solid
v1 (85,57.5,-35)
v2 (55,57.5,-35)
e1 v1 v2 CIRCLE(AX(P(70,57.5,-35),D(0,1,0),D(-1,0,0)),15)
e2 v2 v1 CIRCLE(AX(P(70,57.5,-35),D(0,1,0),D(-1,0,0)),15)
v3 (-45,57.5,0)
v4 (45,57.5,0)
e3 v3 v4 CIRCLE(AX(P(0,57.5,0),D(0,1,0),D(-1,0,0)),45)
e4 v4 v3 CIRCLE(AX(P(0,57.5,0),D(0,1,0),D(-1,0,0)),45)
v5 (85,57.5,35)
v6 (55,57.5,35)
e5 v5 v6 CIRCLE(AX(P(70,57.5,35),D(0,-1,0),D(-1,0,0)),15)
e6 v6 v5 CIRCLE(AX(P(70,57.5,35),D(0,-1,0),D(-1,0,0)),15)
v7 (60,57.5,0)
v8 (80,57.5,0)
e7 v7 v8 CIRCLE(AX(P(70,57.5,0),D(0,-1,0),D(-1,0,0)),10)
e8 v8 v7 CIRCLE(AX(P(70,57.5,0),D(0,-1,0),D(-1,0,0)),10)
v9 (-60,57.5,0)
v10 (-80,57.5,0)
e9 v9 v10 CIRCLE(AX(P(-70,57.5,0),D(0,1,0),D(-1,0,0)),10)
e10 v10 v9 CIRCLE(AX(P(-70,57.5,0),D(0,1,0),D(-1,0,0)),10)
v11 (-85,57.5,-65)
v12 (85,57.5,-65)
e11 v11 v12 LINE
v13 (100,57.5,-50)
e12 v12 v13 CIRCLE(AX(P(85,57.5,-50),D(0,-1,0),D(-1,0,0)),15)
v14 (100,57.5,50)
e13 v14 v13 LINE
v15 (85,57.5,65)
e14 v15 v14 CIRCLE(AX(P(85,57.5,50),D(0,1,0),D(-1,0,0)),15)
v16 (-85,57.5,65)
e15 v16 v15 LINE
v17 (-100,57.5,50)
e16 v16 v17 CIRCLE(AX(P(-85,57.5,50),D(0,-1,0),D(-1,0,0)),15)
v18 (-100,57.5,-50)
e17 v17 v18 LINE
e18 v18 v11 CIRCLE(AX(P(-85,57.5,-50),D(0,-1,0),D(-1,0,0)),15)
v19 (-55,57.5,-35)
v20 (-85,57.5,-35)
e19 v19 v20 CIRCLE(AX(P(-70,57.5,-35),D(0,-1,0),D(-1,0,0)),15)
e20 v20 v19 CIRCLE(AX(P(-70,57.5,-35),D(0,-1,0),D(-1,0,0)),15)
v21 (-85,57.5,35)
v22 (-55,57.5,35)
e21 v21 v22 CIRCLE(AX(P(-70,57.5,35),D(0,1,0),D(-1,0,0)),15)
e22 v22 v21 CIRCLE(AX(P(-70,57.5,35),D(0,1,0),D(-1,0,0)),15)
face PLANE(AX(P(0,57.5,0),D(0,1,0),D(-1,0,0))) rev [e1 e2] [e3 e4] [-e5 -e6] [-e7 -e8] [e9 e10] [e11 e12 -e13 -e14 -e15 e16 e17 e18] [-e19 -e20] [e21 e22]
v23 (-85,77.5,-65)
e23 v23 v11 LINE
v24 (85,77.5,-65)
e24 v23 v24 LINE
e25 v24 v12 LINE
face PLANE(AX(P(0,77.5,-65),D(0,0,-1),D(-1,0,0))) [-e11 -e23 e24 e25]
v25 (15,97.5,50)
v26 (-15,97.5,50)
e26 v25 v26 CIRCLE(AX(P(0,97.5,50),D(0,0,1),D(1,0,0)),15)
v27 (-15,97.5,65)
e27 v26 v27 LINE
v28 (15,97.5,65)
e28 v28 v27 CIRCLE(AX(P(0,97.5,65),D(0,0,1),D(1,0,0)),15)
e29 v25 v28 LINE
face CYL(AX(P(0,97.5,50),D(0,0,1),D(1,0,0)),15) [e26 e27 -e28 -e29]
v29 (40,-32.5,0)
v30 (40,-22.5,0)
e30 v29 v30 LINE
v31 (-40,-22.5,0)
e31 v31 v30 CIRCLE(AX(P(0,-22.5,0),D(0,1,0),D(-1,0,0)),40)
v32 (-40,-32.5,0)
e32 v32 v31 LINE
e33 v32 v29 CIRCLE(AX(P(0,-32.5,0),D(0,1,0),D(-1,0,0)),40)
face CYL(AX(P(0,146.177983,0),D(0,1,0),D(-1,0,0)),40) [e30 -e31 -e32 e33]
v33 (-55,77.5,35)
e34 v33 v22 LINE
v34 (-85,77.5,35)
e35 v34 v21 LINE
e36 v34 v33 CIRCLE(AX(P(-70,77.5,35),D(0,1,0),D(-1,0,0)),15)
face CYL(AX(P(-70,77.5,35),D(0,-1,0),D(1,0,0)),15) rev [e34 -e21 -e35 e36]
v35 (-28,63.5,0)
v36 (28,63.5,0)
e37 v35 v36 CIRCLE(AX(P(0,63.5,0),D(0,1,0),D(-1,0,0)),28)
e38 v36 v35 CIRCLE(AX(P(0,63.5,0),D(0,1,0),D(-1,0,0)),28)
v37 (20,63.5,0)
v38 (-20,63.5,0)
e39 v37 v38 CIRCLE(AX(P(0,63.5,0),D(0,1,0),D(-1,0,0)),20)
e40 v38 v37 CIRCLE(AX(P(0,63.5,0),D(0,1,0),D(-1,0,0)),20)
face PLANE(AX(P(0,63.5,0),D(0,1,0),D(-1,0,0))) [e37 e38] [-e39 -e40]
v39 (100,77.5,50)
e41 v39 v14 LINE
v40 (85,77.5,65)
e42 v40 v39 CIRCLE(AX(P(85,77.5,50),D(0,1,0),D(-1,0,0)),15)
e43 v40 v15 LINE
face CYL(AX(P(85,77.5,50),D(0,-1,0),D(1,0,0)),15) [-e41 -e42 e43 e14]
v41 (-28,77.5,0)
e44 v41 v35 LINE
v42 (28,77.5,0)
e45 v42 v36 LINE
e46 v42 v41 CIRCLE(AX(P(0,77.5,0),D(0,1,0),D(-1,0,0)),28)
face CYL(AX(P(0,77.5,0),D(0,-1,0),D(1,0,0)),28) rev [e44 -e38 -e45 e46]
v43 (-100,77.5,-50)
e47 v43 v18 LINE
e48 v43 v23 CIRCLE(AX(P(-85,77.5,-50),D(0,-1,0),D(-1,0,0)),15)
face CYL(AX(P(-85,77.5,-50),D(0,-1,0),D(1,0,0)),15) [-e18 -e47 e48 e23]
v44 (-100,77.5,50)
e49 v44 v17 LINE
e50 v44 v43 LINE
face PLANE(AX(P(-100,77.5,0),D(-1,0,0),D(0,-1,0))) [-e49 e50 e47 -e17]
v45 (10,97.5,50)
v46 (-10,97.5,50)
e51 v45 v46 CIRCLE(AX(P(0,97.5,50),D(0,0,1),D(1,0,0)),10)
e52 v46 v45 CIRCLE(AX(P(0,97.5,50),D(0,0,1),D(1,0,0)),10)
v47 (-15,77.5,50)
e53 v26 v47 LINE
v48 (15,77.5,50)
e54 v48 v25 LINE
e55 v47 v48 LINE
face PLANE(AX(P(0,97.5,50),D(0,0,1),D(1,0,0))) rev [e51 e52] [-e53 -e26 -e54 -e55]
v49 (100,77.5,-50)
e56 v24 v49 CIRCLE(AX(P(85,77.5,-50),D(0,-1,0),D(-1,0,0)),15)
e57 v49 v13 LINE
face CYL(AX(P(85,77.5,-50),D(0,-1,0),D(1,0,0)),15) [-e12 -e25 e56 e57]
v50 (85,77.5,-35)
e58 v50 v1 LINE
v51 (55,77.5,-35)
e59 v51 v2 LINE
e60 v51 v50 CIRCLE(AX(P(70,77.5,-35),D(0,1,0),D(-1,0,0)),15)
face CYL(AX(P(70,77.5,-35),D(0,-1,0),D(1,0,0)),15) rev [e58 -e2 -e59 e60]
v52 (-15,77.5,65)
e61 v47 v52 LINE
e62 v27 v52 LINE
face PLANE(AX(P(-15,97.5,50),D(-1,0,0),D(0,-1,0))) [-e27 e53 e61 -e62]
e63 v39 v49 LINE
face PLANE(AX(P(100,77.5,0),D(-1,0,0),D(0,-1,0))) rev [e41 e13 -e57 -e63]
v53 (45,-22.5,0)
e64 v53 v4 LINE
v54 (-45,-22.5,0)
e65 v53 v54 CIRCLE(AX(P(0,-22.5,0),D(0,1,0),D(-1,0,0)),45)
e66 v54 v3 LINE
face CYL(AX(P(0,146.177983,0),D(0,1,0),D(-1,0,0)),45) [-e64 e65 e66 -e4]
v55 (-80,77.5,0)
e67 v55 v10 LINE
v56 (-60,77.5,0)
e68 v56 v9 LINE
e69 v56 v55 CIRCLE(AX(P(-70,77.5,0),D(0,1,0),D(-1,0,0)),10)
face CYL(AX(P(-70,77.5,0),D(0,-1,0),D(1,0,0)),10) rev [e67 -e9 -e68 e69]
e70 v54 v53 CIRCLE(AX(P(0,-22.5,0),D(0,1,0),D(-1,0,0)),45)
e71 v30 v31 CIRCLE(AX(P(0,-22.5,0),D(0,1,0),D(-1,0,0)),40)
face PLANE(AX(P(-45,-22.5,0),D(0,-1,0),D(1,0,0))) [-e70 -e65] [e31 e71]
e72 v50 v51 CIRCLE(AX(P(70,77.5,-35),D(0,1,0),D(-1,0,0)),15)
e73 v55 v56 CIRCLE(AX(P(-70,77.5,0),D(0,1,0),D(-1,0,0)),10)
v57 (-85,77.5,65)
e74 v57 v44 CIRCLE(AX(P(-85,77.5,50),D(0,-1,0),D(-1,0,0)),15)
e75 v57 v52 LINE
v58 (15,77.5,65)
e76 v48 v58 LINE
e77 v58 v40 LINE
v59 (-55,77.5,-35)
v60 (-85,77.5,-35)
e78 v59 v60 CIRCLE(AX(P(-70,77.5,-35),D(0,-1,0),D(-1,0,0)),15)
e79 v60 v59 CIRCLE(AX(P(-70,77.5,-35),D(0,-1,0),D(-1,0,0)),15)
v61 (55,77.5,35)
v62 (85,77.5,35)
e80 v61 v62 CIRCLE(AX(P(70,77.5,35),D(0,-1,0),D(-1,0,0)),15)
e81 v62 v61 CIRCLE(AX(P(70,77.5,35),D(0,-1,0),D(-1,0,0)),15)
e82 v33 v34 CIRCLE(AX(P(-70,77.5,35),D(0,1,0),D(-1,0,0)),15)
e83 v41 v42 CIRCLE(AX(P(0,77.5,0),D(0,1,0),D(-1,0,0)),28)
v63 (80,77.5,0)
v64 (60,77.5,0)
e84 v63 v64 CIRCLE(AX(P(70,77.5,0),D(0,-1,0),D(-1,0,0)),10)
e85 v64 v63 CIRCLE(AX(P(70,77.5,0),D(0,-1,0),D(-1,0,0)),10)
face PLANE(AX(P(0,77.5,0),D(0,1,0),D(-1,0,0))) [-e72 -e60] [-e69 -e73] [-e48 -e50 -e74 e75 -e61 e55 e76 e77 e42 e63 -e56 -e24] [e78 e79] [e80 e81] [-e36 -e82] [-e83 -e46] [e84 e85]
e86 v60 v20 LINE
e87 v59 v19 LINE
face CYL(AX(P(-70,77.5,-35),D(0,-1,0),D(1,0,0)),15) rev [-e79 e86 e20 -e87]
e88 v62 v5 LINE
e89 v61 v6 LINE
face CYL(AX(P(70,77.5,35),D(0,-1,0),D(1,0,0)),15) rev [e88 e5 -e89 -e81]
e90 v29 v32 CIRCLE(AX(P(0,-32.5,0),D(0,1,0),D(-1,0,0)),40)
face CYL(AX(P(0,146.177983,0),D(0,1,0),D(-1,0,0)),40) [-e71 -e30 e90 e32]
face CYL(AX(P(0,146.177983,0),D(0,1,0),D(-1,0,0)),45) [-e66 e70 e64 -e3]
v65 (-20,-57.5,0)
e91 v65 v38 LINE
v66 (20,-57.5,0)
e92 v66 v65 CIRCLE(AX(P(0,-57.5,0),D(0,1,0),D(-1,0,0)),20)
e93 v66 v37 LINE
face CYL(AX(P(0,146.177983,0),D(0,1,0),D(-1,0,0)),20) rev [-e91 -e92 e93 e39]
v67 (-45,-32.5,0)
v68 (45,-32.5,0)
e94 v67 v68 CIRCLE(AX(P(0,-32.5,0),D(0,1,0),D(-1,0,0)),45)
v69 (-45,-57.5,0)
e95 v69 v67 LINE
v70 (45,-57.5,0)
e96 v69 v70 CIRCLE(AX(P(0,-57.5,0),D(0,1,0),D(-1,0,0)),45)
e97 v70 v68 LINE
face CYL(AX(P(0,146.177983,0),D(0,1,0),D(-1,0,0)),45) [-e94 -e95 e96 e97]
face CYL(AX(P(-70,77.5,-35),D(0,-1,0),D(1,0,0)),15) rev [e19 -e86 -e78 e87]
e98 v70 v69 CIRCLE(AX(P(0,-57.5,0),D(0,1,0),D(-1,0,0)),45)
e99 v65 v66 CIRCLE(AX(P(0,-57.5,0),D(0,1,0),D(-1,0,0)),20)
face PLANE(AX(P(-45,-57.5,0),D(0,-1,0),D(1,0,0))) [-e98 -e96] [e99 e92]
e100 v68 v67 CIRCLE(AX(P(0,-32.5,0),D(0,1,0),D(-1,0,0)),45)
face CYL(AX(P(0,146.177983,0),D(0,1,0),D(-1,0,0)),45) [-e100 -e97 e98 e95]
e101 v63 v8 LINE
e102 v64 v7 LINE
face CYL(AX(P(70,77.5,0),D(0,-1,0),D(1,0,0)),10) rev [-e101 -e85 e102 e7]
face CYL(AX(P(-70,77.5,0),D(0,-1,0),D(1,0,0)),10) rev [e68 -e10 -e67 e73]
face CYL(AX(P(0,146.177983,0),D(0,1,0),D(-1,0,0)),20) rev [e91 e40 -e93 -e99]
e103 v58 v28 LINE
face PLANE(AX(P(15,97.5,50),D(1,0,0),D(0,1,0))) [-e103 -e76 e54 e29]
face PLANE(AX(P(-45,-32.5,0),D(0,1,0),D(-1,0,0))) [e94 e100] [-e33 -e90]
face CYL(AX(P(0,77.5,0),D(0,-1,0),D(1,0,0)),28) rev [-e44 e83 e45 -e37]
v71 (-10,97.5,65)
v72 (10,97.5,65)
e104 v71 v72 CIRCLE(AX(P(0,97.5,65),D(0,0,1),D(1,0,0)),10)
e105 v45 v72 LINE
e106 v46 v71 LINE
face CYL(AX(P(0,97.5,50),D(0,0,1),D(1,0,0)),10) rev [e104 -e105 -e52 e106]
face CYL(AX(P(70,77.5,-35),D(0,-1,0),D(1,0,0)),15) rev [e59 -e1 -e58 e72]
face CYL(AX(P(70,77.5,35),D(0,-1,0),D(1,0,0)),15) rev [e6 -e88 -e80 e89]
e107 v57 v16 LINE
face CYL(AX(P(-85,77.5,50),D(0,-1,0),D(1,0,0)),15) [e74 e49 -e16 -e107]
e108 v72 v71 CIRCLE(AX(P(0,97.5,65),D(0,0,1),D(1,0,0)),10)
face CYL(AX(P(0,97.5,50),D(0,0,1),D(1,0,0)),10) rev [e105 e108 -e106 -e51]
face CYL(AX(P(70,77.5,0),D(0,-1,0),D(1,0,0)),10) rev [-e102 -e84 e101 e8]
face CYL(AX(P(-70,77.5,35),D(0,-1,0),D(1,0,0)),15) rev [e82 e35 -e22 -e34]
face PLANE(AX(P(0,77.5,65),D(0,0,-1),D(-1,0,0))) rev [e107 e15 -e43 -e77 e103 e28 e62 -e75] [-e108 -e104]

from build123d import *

# Parameters (mm, degrees)
MOUNTING_PLATE_SKETCH_R         = 15
MOUNTING_PLATE_SKETCH_R_2       = 10
MOUNTING_PLATE_SKETCH_R_3       = 45
MOUNTING_PLATE_SKETCH_R_4       = 28
MOUNTING_PLATE_200X130X20_DEPTH = 20
PIVOT_LUG_SKETCH_R              = 10
PIVOT_LUG_DEPTH                 = 15
RING_BOSS_SKETCH_R              = 28
RING_BOSS_SKETCH_R_2            = 20
RING_BOSS_6MM_DEPTH             = 6


with BuildPart() as part:
    # Shaft Profile Sketch → Grooved Shaft Revolve (revolve)
    with BuildSketch(Plane.XY):
        Polygon((-45, 57.5), (-45, -22.5), (-40, -22.5), (-40, -32.5), (-45, -32.5), (-45, -57.5), (-20, -57.5), (-20, 57.5), align=None)
    revolve(axis=Axis((0, 146.177983413, 0), (0, -1, 0)))

    # Mounting Plate Sketch → Mounting Plate 200x130x20 (add)
    # profile 1 of 2: a face of its own
    with BuildSketch(Plane(origin=(0, 57.5, 0), x_dir=(1, 0, 0), z_dir=(0, 1, 0))):
        with BuildLine():
            ThreePointArc((85, 65), (95.606601718, 60.606601718), (100, 50))
            Line((100, 50), (100, -50))
            ThreePointArc((100, -50), (95.606601718, -60.606601718), (85, -65))
            Line((85, -65), (-85, -65))
            ThreePointArc((-85, -65), (-95.606601718, -60.606601718), (-100, -50))
            Line((-100, -50), (-100, 50))
            ThreePointArc((-100, 50), (-95.606601718, 60.606601718), (-85, 65))
            Line((-85, 65), (85, 65))
        make_face()
        with Locations(Location((70, 35, 0), (0, 0, 180))):
            Circle(MOUNTING_PLATE_SKETCH_R, mode=Mode.SUBTRACT)
        with Locations(Location((70, -35, 0), (0, 0, 180))):
            Circle(MOUNTING_PLATE_SKETCH_R, mode=Mode.SUBTRACT)
        with Locations(Location((-70, 0, 0), (0, 0, 180))):
            Circle(MOUNTING_PLATE_SKETCH_R_2, mode=Mode.SUBTRACT)
        with Locations(Location((-70, -35, 0), (0, 0, 180))):
            Circle(MOUNTING_PLATE_SKETCH_R, mode=Mode.SUBTRACT)
        with Locations(Location((-70, 35, 0), (0, 0, 180))):
            Circle(MOUNTING_PLATE_SKETCH_R, mode=Mode.SUBTRACT)
        with Locations(Location((70, 0, 0), (0, 0, 180))):
            Circle(MOUNTING_PLATE_SKETCH_R_2, mode=Mode.SUBTRACT)
        with Locations(Location((0, 0, 0), (0, 0, 180))):
            Circle(MOUNTING_PLATE_SKETCH_R_3, mode=Mode.SUBTRACT)
    # profile 2 of 2: a face of its own
    with BuildSketch(Plane(origin=(0, 57.5, 0), x_dir=(1, 0, 0), z_dir=(0, 1, 0))):
        with Locations(Location((0, 0, 0), (0, 0, 180))):
            Circle(MOUNTING_PLATE_SKETCH_R_3)
        with Locations(Location((0, 0, 0), (0, 0, 180))):
            Circle(MOUNTING_PLATE_SKETCH_R_4, mode=Mode.SUBTRACT)
    extrude(amount=MOUNTING_PLATE_200X130X20_DEPTH)

    # Pivot Lug Sketch → Pivot Lug (add)
    with BuildSketch(Plane.XY.offset(65)):
        with BuildLine():
            Line((15, 97.5), (15, 77.5))
            Line((15, 77.5), (-15, 77.5))
            Line((-15, 77.5), (-15, 97.5))
            ThreePointArc((-15, 97.5), (0, 112.5), (15, 97.5))
        make_face()
        with Locations((0, 97.5)):
            Circle(PIVOT_LUG_SKETCH_R, mode=Mode.SUBTRACT)
    extrude(amount=-PIVOT_LUG_DEPTH)

    # Ring Boss Sketch → Ring Boss 6mm (add)
    with BuildSketch(Plane(origin=(0, 57.5, 0), x_dir=(1, 0, 0), z_dir=(0, 1, 0))):
        with Locations(Location((0, 0, 0), (0, 0, 180))):
            Circle(RING_BOSS_SKETCH_R)
        with Locations(Location((0, 0, 0), (0, 0, 180))):
            Circle(RING_BOSS_SKETCH_R_2, mode=Mode.SUBTRACT)
    extrude(amount=RING_BOSS_6MM_DEPTH)


solid = part.part
